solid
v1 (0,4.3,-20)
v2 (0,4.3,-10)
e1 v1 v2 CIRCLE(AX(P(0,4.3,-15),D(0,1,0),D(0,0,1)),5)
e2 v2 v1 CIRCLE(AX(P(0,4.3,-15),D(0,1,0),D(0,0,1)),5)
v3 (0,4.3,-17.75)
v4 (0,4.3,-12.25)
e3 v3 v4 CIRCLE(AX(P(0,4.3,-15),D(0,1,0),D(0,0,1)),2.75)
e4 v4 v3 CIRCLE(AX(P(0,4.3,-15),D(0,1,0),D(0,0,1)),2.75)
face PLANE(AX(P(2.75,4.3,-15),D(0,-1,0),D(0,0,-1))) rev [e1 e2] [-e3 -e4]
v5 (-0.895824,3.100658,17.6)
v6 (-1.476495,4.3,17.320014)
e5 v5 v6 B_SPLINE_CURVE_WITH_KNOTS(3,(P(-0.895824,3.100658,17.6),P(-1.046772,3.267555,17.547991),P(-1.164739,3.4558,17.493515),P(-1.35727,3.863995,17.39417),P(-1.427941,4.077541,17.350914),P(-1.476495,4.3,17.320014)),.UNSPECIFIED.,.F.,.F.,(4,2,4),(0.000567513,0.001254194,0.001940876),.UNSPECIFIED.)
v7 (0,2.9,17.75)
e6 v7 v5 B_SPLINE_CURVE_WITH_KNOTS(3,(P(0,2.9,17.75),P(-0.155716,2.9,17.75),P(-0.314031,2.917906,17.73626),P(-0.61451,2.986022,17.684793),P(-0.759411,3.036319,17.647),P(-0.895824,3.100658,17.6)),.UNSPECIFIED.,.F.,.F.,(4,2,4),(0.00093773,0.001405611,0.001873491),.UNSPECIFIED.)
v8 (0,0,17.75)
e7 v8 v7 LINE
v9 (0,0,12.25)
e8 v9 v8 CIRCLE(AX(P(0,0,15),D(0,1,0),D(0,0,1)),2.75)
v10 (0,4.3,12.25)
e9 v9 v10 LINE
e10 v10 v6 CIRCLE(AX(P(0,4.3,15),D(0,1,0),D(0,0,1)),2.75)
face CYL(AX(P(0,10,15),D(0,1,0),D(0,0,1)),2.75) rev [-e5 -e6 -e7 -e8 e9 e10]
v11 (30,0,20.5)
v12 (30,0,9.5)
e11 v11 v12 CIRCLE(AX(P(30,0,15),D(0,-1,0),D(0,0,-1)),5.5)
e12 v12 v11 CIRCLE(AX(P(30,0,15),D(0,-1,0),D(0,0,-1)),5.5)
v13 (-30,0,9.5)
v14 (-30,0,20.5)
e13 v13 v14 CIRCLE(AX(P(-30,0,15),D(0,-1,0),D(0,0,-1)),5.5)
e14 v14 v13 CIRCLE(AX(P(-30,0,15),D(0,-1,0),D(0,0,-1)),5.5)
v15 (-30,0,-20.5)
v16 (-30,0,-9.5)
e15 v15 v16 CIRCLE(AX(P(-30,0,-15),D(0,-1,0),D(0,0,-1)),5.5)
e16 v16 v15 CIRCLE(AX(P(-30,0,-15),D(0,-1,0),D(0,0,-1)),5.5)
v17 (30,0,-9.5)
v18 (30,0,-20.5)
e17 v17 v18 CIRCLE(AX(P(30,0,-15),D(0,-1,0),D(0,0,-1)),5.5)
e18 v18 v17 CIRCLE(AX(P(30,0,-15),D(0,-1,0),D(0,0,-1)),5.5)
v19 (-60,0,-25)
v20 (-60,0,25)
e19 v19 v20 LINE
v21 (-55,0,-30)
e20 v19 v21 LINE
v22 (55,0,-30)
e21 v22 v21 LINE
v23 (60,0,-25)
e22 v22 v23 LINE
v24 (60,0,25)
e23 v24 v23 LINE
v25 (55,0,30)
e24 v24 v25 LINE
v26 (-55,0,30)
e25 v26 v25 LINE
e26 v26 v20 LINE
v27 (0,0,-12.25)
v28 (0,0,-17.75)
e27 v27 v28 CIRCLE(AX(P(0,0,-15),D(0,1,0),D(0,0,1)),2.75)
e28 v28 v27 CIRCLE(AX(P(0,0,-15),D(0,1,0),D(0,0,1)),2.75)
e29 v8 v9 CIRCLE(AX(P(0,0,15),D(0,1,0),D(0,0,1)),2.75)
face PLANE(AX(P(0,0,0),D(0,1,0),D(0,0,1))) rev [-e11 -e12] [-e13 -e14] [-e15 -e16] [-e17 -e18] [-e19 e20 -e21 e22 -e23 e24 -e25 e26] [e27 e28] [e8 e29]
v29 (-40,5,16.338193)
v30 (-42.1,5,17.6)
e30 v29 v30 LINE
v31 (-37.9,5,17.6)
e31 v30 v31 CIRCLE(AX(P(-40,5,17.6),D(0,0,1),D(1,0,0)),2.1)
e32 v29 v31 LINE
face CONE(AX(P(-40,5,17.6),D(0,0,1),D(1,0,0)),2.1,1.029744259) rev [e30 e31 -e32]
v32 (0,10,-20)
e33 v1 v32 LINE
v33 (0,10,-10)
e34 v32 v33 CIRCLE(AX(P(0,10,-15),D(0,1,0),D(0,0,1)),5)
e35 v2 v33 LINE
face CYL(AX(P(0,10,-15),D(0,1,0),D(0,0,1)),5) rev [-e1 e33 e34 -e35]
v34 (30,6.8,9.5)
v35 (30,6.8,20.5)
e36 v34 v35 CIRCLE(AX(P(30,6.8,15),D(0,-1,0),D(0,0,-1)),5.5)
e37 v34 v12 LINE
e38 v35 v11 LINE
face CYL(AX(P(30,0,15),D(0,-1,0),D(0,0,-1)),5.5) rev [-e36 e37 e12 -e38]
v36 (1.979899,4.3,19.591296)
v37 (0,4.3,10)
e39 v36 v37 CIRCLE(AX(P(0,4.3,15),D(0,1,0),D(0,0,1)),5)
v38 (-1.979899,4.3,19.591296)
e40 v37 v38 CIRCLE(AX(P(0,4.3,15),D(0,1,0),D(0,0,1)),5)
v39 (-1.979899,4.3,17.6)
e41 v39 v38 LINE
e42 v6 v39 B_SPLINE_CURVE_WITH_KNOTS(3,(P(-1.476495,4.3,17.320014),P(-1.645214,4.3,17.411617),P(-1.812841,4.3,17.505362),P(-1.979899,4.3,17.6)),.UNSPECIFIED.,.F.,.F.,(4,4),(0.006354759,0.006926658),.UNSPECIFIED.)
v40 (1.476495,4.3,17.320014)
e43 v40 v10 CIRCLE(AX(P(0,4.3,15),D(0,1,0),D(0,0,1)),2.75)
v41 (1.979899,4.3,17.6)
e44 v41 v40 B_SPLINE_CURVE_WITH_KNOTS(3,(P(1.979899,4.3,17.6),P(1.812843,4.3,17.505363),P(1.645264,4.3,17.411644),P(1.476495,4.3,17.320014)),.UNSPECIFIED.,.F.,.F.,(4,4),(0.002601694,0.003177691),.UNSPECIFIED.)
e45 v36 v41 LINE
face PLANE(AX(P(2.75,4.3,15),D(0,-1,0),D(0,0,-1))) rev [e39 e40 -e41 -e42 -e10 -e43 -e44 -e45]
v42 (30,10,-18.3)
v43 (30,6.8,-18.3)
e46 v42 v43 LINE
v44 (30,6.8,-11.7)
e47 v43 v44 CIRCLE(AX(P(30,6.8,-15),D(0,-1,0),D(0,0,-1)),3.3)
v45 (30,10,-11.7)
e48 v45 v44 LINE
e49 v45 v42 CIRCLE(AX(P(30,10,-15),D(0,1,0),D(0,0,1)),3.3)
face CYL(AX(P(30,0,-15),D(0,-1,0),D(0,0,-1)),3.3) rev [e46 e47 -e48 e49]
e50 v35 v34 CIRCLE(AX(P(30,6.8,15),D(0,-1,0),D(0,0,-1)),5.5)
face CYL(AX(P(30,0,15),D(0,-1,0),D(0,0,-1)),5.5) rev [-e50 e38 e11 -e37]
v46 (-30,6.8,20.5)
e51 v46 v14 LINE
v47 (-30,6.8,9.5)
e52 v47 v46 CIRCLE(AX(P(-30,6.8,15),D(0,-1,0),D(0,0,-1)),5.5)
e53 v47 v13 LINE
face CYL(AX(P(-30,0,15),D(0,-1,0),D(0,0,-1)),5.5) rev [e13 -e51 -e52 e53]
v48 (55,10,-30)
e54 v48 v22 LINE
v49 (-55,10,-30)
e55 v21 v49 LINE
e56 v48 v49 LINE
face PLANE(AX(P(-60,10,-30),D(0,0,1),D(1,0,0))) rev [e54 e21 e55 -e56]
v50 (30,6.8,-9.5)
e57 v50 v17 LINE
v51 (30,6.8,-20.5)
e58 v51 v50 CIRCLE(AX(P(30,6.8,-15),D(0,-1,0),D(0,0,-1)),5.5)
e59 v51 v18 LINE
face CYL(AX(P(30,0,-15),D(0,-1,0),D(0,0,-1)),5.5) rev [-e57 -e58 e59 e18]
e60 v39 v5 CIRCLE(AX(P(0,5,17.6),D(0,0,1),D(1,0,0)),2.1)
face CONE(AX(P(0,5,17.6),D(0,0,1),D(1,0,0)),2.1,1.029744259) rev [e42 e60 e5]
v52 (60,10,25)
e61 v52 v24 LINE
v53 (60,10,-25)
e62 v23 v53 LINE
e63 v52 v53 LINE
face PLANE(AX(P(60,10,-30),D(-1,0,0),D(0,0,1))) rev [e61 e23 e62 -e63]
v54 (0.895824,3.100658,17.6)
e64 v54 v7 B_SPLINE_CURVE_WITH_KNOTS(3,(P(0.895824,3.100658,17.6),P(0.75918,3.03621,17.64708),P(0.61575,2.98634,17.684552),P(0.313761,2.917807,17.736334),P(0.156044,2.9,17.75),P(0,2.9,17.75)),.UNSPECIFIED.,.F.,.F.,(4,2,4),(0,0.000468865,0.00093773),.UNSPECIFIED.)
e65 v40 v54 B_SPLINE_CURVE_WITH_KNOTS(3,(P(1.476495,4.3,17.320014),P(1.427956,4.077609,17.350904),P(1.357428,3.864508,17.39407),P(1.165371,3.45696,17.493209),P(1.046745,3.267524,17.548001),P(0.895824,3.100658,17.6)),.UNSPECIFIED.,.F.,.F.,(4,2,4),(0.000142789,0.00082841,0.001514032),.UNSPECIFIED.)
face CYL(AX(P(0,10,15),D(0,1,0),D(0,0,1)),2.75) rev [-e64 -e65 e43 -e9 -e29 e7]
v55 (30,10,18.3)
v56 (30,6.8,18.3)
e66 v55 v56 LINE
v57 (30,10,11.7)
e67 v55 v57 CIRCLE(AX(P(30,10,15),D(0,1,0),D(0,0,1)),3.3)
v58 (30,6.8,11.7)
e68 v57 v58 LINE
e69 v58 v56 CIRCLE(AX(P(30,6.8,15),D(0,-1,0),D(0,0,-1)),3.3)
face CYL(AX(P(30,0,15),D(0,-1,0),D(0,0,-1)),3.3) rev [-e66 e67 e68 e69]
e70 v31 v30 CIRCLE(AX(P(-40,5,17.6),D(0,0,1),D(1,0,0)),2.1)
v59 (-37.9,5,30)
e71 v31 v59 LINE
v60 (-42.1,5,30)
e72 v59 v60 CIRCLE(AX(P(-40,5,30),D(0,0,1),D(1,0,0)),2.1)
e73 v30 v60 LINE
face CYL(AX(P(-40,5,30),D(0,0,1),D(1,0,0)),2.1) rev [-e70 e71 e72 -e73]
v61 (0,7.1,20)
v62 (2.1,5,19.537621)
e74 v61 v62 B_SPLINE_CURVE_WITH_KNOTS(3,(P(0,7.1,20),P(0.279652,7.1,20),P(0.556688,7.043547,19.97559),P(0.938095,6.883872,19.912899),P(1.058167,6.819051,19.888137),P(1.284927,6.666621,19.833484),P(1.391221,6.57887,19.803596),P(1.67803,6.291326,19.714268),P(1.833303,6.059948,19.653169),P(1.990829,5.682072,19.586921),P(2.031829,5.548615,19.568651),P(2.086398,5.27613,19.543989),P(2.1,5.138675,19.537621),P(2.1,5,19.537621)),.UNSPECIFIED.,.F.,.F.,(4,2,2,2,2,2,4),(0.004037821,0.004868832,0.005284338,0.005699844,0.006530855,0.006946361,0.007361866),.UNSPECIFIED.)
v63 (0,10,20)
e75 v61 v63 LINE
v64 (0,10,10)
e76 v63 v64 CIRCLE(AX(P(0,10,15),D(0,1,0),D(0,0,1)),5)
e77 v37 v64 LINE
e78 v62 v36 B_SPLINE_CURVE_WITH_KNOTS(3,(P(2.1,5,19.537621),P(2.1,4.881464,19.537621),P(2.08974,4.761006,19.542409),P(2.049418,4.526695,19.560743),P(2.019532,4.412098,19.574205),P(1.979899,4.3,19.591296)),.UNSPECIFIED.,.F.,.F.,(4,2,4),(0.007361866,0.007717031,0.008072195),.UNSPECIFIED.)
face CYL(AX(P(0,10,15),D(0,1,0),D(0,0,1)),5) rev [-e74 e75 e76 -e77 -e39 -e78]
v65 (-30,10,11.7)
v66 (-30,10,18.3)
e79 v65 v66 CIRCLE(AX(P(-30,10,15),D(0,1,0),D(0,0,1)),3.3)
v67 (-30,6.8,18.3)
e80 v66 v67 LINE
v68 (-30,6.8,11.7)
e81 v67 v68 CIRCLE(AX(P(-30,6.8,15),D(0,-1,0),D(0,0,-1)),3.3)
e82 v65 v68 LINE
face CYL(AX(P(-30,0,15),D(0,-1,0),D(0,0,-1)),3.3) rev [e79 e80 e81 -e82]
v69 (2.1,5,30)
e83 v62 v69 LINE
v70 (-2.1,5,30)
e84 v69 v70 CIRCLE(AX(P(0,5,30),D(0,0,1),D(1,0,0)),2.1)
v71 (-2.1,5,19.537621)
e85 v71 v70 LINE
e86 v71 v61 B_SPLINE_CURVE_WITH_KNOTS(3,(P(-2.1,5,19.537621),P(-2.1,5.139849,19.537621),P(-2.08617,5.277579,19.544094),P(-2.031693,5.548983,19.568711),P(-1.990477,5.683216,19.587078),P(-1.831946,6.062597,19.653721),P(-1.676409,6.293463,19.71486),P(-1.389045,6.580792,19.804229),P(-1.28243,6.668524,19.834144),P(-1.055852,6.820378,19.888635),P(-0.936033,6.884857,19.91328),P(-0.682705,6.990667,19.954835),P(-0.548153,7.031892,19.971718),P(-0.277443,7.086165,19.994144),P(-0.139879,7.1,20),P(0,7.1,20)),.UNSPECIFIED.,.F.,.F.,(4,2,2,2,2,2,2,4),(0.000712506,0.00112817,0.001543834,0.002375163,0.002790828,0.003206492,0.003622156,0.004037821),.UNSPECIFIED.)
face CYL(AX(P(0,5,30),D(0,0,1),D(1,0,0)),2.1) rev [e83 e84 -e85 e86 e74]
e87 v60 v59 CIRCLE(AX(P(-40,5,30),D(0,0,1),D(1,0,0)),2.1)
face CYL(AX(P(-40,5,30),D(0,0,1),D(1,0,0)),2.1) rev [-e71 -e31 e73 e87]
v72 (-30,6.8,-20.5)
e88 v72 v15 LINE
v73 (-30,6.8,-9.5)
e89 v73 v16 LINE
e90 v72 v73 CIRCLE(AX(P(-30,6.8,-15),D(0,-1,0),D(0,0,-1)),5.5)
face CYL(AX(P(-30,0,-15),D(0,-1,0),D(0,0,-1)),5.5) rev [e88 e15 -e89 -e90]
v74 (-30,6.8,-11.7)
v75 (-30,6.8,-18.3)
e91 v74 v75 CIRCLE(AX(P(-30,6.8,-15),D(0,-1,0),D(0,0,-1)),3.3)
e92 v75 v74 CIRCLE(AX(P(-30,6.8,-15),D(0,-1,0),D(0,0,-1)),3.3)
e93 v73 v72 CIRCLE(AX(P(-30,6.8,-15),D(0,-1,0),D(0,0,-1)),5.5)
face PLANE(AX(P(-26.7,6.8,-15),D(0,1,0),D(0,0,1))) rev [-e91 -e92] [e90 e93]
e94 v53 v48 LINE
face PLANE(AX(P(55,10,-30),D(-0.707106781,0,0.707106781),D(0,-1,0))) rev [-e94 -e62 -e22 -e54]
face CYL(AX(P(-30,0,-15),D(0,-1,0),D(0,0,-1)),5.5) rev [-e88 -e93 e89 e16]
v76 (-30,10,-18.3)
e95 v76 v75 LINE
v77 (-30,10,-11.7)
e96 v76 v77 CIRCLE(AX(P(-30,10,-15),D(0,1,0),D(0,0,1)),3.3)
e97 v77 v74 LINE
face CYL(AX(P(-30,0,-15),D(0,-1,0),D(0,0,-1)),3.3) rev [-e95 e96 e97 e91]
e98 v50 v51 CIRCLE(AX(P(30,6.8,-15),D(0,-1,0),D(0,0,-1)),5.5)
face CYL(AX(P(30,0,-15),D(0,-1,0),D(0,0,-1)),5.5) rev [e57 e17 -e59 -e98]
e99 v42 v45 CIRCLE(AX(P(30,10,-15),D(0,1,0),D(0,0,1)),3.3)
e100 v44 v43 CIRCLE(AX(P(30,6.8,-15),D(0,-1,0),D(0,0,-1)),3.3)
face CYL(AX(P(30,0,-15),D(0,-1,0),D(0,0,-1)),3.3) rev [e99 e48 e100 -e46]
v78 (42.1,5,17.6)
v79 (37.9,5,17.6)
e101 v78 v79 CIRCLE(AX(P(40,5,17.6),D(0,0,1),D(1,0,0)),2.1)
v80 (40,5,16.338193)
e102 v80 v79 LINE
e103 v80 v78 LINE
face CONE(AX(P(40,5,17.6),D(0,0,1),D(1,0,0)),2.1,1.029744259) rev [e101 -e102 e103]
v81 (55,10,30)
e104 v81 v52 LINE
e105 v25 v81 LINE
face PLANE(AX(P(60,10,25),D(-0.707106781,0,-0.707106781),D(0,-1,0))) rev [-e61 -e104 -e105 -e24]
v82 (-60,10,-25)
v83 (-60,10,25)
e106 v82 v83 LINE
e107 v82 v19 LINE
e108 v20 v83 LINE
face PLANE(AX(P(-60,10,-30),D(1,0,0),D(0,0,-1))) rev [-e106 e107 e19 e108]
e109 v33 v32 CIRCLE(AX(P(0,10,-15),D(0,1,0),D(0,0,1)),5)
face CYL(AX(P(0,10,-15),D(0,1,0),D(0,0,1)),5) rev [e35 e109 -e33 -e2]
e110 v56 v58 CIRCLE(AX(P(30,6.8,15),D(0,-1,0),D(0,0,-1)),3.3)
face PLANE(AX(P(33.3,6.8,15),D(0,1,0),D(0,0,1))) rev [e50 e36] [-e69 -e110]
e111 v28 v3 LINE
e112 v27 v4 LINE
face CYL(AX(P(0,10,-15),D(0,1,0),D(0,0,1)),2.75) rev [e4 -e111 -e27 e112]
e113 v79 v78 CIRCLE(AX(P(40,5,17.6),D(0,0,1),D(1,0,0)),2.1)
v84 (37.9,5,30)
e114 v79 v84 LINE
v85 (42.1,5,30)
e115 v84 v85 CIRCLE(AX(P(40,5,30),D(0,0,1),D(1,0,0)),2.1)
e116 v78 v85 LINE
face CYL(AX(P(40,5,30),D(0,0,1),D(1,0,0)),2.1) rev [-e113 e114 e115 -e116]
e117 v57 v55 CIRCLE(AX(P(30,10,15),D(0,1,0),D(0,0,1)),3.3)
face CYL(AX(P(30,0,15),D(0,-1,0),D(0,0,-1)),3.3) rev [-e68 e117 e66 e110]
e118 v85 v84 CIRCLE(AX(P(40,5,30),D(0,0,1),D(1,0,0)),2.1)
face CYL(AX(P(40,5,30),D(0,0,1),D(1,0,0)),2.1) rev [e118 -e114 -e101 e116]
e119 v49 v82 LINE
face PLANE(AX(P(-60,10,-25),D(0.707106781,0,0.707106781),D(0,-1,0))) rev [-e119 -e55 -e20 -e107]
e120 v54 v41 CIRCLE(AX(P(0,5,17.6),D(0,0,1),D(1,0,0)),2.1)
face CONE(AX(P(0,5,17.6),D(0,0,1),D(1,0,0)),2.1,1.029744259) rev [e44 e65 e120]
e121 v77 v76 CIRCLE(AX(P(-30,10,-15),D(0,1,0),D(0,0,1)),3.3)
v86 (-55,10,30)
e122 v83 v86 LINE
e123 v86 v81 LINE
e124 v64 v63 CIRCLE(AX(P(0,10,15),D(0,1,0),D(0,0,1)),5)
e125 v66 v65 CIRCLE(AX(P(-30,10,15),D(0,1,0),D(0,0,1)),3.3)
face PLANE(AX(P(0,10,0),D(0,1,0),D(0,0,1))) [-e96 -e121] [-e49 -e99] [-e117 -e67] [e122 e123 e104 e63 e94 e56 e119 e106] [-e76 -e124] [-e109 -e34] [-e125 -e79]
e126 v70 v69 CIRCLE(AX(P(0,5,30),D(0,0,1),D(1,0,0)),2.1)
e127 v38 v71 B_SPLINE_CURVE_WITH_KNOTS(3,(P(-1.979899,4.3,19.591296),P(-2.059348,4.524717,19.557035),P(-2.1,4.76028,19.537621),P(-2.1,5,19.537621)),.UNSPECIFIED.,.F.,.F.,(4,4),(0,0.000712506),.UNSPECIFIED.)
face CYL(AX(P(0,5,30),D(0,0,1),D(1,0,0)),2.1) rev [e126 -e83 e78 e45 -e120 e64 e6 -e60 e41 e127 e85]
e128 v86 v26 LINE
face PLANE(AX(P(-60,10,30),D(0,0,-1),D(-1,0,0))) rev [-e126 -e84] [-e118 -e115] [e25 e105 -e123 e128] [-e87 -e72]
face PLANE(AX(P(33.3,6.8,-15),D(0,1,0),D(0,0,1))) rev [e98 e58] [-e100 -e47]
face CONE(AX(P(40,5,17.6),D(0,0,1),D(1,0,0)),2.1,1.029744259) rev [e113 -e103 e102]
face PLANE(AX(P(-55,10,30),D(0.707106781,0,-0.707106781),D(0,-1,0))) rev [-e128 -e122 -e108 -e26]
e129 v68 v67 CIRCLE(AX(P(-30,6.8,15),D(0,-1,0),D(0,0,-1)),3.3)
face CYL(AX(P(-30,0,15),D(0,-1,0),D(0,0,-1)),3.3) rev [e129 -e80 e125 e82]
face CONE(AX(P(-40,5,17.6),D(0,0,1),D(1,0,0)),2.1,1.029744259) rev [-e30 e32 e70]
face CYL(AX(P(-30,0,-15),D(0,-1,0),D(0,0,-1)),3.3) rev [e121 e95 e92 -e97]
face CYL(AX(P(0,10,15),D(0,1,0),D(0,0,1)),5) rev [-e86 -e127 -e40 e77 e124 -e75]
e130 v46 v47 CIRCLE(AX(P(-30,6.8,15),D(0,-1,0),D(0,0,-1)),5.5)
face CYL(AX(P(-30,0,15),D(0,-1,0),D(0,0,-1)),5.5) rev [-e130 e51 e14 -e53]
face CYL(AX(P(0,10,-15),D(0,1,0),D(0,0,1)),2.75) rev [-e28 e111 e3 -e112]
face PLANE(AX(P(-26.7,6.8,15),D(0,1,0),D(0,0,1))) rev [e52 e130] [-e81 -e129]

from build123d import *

# Parameters (mm, degrees)
SKETCH_1_W                = 120
SKETCH_1_H                = 60
EXTRUDE_1_DEPTH           = 10
CHAMFER_1_SIZE            = 5
HOLE_WIZARD_M5_1_D        = 4.2
HOLE_WIZARD_M5_1_DEPTH    = 12.4
HOLE_WIZARD_M5_1_TIP      = 1.2618073
HOLE_WIZARD_1_D           = 6.6
HOLE_WIZARD_1_DEPTH       = 12.4
HOLE_WIZARD_1_CBORE_D     = 11
HOLE_WIZARD_1_CBORE_DEPTH = 6.8
HOLE_WIZARD_1_TIP         = 1.982840043
HOLE_WIZARD_2_D           = 5.5
HOLE_WIZARD_2_DEPTH       = 12.4
HOLE_WIZARD_2_CBORE_D     = 10
HOLE_WIZARD_2_CBORE_DEPTH = 5.7
HOLE_WIZARD_2_TIP         = 1.652366702


with BuildPart() as part:
    # 草图1 → 凸台-拉伸1 (new body)
    with BuildSketch(Plane(origin=(0, 0, 0), x_dir=(1, 0, 0), z_dir=(0, 1, 0))):
        Rectangle(SKETCH_1_W, SKETCH_1_H)
    extrude(amount=EXTRUDE_1_DEPTH)

    # 倒角1
    chamfer_1_edges = [part.edges().sort_by_distance(p)[0] for p in [
        (60, 5, 30),
        (-60, 5, 30),
        (-60, 5, -30),
        (60, 5, -30),
    ]]
    chamfer(chamfer_1_edges, length=CHAMFER_1_SIZE)

    # M5 螺纹孔1
    with Locations(Plane.XY.offset(30)):
        with Locations((-40, 5), (0, 5), (40, 5)):
            Hole(HOLE_WIZARD_M5_1_D / 2, depth=HOLE_WIZARD_M5_1_DEPTH)
            with Locations((0, 0, -(HOLE_WIZARD_M5_1_DEPTH + HOLE_WIZARD_M5_1_TIP / 2))):  # 118° drill point
                Cone(0, HOLE_WIZARD_M5_1_D / 2, HOLE_WIZARD_M5_1_TIP, mode=Mode.SUBTRACT)

    # 打孔尺寸(%根据)内六角圆柱头螺钉的类型1
    with Locations(Plane(origin=(0, 0, 0), x_dir=(-1, 0, 0), z_dir=(0, -1, 0))):
        with Locations((30, -15), (30, 15), (-30, -15), (-30, 15)):
            CounterBoreHole(HOLE_WIZARD_1_D / 2, HOLE_WIZARD_1_CBORE_D / 2, HOLE_WIZARD_1_CBORE_DEPTH, depth=HOLE_WIZARD_1_DEPTH)
            with Locations((0, 0, -(HOLE_WIZARD_1_DEPTH + HOLE_WIZARD_1_TIP / 2))):  # 118° drill point
                Cone(0, HOLE_WIZARD_1_D / 2, HOLE_WIZARD_1_TIP, mode=Mode.SUBTRACT)

    # 打孔尺寸(%根据)内六角圆柱头螺钉的类型2
    with Locations(Plane(origin=(0, 10, 0), x_dir=(1, 0, 0), z_dir=(0, 1, 0))):
        with Locations((0, -15), (0, 15)):
            CounterBoreHole(HOLE_WIZARD_2_D / 2, HOLE_WIZARD_2_CBORE_D / 2, HOLE_WIZARD_2_CBORE_DEPTH, depth=HOLE_WIZARD_2_DEPTH)
            with Locations((0, 0, -(HOLE_WIZARD_2_DEPTH + HOLE_WIZARD_2_TIP / 2))):  # 118° drill point
                Cone(0, HOLE_WIZARD_2_D / 2, HOLE_WIZARD_2_TIP, mode=Mode.SUBTRACT)


solid = part.part
